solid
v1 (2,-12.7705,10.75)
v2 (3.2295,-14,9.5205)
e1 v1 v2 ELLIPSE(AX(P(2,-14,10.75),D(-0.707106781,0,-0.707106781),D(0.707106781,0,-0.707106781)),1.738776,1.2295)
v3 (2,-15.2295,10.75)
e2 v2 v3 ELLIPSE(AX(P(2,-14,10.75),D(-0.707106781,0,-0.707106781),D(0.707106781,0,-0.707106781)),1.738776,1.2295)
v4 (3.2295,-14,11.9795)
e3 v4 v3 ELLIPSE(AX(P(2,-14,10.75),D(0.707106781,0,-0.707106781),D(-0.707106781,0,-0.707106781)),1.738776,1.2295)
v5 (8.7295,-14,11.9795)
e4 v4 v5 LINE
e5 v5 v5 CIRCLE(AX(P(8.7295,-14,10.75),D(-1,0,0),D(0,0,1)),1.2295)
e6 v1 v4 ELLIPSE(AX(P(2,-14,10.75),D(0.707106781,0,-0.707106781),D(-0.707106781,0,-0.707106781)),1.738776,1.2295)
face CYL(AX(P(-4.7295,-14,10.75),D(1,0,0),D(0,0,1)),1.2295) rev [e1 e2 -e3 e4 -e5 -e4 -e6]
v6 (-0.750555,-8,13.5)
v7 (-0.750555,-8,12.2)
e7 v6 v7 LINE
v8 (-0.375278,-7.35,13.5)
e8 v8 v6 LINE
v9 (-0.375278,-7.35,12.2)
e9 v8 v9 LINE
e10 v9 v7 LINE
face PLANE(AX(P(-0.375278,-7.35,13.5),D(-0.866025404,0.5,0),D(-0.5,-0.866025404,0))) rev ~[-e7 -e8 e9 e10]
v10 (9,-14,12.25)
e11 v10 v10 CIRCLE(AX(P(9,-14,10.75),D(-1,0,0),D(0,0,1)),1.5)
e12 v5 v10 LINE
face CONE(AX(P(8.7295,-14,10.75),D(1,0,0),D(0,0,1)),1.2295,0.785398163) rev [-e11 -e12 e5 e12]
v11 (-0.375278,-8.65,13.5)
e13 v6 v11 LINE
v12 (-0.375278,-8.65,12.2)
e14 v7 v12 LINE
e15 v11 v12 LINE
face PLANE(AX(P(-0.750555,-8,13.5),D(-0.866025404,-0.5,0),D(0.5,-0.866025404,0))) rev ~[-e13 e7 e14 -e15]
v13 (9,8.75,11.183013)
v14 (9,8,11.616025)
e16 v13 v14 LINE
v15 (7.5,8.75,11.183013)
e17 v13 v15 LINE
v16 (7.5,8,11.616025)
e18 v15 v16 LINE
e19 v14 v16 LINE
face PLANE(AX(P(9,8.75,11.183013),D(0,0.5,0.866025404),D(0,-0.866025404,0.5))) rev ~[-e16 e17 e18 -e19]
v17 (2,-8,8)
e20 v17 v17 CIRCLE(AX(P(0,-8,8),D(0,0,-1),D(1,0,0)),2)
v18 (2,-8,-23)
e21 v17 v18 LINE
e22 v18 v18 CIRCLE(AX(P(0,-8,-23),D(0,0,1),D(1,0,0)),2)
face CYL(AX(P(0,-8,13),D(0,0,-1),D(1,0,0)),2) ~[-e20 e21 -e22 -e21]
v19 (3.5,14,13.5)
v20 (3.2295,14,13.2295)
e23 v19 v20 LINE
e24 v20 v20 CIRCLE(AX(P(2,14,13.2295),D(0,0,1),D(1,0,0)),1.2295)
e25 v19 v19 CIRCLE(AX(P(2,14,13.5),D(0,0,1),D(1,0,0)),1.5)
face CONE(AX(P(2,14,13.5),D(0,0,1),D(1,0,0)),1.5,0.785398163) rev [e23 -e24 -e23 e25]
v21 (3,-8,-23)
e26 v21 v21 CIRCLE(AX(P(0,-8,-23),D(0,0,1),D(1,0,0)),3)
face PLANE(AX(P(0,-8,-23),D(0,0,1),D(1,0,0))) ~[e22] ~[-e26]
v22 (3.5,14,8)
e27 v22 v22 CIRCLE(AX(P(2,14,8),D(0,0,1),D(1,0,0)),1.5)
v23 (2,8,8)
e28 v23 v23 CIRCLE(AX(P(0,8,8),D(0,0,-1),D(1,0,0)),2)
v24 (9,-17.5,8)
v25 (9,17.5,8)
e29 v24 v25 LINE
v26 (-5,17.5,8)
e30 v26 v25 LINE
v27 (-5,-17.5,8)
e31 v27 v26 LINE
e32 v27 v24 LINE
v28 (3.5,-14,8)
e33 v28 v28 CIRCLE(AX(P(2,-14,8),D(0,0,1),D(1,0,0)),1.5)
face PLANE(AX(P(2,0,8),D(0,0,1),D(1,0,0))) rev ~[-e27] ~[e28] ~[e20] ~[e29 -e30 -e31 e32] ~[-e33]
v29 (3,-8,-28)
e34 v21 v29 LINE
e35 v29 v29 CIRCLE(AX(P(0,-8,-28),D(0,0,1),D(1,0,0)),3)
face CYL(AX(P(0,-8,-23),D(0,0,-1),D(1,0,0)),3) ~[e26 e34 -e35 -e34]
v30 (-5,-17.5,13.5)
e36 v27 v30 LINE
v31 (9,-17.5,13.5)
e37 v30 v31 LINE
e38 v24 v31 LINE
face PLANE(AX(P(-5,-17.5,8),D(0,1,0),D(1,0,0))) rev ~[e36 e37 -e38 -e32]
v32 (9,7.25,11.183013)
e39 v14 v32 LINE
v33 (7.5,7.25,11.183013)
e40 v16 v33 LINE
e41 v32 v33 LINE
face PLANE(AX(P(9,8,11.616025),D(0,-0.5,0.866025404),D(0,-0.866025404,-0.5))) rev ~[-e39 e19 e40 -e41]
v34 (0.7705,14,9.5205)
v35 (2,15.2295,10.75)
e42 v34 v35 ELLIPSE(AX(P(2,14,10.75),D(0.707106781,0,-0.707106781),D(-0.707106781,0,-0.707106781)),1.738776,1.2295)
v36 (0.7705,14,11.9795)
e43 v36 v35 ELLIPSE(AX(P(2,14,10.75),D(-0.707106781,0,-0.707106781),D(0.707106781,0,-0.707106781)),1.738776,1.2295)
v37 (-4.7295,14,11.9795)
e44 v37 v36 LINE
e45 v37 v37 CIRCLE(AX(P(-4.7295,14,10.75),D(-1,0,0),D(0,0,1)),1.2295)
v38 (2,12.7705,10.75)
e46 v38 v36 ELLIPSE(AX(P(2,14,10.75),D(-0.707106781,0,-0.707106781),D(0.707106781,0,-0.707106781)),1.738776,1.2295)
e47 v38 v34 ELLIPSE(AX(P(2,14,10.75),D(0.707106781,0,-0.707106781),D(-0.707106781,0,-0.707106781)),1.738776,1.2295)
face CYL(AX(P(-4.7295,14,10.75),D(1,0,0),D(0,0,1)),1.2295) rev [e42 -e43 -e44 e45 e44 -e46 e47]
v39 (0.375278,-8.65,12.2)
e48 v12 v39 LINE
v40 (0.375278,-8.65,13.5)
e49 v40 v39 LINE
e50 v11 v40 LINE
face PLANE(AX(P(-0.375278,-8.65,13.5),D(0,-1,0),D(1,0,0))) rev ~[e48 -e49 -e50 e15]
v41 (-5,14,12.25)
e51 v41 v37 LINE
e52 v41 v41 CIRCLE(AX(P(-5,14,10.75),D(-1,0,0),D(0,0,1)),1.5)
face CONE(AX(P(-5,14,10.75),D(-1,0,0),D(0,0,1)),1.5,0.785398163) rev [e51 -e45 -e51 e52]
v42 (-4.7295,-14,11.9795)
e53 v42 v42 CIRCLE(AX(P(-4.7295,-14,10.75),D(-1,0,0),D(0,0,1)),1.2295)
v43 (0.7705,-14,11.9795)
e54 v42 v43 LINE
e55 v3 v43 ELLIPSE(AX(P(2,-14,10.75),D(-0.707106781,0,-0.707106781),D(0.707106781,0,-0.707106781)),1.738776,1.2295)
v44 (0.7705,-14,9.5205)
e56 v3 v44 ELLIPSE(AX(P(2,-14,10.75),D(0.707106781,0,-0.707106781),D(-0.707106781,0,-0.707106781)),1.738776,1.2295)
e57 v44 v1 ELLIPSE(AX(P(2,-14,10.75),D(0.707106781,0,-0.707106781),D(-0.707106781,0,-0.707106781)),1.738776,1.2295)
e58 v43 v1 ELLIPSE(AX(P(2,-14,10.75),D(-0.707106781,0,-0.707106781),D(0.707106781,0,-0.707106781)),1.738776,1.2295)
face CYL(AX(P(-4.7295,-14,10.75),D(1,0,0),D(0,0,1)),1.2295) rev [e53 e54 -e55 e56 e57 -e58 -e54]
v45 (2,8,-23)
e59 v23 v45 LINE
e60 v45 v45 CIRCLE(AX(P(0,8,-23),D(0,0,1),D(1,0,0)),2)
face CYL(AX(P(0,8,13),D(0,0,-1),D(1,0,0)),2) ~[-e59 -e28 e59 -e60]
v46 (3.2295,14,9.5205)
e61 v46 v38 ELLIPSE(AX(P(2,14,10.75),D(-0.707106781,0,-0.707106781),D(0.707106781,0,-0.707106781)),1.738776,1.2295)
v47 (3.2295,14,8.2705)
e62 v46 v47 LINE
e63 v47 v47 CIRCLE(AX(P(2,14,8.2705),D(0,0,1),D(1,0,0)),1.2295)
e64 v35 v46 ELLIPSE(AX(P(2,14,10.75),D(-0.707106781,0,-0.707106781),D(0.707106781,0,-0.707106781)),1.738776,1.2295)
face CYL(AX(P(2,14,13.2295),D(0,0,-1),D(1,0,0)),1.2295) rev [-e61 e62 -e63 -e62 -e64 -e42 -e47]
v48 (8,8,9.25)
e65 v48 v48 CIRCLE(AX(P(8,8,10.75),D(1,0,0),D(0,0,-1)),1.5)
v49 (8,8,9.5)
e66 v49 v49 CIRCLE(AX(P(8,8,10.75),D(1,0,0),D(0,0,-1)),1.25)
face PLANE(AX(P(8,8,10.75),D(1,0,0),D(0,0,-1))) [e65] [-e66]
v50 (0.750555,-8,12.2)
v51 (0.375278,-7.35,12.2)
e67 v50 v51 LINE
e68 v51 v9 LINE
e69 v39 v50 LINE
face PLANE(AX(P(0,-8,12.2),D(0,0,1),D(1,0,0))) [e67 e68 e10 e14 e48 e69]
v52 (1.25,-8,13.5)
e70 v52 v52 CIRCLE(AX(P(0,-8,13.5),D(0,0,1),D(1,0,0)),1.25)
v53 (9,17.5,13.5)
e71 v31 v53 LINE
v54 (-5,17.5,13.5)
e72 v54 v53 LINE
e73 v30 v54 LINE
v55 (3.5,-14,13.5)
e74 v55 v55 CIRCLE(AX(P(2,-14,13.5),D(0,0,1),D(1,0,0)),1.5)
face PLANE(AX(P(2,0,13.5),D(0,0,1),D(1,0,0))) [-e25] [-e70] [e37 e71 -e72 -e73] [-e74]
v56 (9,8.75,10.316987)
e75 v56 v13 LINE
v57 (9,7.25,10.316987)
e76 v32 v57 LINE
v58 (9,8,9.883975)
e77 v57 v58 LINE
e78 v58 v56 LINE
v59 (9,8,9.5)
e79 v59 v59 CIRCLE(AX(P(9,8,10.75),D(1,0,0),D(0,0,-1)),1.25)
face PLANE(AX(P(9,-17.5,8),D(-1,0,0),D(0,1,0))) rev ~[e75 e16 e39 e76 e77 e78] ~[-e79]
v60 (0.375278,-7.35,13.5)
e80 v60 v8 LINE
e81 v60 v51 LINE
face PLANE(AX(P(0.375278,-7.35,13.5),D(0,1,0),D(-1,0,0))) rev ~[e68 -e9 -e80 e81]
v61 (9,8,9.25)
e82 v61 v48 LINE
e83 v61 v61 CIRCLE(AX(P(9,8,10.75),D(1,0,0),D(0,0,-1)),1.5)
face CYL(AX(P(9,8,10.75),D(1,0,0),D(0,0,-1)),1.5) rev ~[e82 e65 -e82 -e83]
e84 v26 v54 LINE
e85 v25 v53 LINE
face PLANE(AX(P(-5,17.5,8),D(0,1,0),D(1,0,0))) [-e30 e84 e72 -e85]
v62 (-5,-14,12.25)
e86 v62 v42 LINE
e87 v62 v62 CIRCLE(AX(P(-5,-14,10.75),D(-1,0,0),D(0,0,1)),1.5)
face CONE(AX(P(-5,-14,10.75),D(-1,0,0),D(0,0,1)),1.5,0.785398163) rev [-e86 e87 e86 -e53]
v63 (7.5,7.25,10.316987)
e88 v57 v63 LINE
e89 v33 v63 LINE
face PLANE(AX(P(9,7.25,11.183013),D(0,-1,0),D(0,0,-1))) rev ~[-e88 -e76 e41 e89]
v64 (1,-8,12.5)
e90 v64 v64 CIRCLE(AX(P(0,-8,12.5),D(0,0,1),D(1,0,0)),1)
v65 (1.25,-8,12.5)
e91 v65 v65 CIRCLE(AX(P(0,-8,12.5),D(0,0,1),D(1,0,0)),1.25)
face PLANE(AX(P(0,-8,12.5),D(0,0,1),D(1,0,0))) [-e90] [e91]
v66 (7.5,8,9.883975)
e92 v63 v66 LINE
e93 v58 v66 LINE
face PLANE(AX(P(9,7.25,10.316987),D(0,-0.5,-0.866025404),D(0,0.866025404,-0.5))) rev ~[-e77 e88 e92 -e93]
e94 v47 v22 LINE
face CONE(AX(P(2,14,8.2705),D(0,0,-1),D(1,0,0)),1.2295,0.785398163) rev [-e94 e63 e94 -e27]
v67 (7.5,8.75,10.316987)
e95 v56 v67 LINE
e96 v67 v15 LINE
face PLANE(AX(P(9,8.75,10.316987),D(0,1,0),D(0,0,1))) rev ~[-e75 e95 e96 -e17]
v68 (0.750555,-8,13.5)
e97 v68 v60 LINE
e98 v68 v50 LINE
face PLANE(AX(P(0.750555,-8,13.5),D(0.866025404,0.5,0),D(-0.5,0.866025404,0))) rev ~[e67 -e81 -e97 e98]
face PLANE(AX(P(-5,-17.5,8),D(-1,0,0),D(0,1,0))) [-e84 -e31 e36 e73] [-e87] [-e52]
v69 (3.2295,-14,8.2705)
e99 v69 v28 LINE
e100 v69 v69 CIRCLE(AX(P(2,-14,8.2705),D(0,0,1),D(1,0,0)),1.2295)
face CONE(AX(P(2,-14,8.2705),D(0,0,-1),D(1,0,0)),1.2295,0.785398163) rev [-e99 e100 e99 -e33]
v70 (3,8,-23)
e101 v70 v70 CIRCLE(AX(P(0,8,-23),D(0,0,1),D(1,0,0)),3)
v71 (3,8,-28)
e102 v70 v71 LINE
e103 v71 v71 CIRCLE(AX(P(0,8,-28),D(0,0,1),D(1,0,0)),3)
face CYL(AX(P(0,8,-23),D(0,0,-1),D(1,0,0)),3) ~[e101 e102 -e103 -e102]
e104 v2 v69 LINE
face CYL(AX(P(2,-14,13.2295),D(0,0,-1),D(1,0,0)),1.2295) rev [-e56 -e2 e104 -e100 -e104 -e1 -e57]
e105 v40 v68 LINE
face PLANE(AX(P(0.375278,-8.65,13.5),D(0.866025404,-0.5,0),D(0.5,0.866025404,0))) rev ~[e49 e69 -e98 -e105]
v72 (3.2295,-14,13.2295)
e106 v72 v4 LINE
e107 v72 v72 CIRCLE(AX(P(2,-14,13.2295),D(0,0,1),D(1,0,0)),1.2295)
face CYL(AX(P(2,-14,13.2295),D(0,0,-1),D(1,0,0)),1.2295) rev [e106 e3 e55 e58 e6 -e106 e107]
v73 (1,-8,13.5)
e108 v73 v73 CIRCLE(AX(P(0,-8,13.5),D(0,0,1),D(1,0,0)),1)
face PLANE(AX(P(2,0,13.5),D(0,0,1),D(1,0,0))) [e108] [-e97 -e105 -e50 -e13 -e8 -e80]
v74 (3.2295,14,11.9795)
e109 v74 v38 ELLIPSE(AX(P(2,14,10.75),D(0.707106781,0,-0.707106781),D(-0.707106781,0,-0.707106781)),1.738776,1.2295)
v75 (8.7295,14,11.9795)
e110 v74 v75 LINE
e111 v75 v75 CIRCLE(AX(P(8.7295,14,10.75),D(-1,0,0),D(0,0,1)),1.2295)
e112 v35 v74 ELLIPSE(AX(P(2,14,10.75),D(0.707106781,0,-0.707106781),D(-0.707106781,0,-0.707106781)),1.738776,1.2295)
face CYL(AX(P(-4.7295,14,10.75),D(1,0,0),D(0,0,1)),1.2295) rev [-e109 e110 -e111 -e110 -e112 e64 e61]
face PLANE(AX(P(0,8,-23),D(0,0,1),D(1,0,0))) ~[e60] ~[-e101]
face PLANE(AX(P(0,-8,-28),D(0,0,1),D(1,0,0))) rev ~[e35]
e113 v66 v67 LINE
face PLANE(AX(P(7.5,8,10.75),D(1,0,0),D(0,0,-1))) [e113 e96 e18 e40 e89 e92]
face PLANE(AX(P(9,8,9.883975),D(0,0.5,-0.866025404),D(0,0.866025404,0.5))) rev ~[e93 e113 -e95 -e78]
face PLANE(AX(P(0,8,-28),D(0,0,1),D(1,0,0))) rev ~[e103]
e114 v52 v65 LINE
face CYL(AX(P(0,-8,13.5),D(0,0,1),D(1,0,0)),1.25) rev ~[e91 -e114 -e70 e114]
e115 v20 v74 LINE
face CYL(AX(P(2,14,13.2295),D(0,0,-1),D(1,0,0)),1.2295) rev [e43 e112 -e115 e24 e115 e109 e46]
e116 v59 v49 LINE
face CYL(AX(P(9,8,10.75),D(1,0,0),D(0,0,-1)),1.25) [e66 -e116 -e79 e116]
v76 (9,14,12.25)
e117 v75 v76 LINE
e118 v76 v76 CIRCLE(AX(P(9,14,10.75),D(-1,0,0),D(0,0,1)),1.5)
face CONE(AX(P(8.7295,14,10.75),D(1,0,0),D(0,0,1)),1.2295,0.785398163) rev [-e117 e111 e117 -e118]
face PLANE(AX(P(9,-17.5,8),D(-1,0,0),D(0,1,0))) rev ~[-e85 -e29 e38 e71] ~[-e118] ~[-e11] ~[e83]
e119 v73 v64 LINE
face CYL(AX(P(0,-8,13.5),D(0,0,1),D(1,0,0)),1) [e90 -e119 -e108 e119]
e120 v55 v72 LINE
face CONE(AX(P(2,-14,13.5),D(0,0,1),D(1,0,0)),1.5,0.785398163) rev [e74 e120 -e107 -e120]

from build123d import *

# Parameters (mm, degrees)
SKETCH1_W           = 14
SKETCH1_H           = 35
BOSS_EXTRUDE1_DEPTH = 5.5
SKETCH8_R           = 1.25
SKETCH8_R_2         = 1
CUT_EXTRUDE1_DEPTH  = 1
CUT_EXTRUDE2_DEPTH  = 1.3
SKETCH10_R          = 1.5
SKETCH10_R_2        = 1.25
CUT_EXTRUDE3_DEPTH  = 1
CUT_EXTRUDE4_DEPTH  = 1.5


with BuildPart() as part:
    # Sketch1 → Boss-Extrude1 (new body)
    with BuildSketch(Plane.XY.offset(8)):
        with Locations((2, 0)):
            Rectangle(SKETCH1_W, SKETCH1_H)
    extrude(amount=BOSS_EXTRUDE1_DEPTH)

    # Sketch2 → Revolve1 (revolve)
    with BuildSketch(Plane(origin=(0, 0, 0), x_dir=(0, 0, -1), z_dir=(1, 0, 0)), mode=Mode.PRIVATE) as revolve1_sk:
        Polygon((-13, 8), (-13, 10), (23, 10), (23, 11), (28, 11), (28, 8), align=None)
    revolve(revolve1_sk.sketch.rotate(Axis((0, 8, -28), (0, 0, 1)), 270), axis=Axis((0, 8, -28), (0, 0, 1)))

    # Sketch3 → Revolve2 (revolve)
    with BuildSketch(Plane(origin=(0, 0, 0), x_dir=(0, 0, -1), z_dir=(1, 0, 0)), mode=Mode.PRIVATE) as revolve2_sk:
        Polygon((-13, -8), (-13, -6), (23, -6), (23, -5), (28, -5), (28, -8), align=None)
    revolve(revolve2_sk.sketch.rotate(Axis((0, -8, -28), (0, 0, 1)), 270), axis=Axis((0, -8, -28), (0, 0, 1)))

    # Sketch4 → Cut-Revolve1 (revolve, cut)
    with BuildSketch(Plane(origin=(2, 0, 0), x_dir=(0, 0, -1), z_dir=(1, 0, 0)), mode=Mode.PRIVATE) as cut_revolve1_sk:
        Polygon((-13.5, 14), (-13.5, 15.5), (-13.2295, 15.2295), (-8.2705, 15.2295), (-8, 15.5), (-8, 14), align=None)
    revolve(cut_revolve1_sk.sketch.rotate(Axis((2, 14, 8), (0, 0, 1)), 270), axis=Axis((2, 14, 8), (0, 0, 1)), mode=Mode.SUBTRACT)

    # Sketch5 → Cut-Revolve2 (revolve, cut)
    with BuildSketch(Plane(origin=(2, 0, 0), x_dir=(0, 0, -1), z_dir=(1, 0, 0)), mode=Mode.PRIVATE) as cut_revolve2_sk:
        Polygon((-13.5, -14), (-13.5, -12.5), (-13.2295, -12.7705), (-8.2705, -12.7705), (-8, -12.5), (-8, -14), align=None)
    revolve(cut_revolve2_sk.sketch.rotate(Axis((2, -14, 8), (0, 0, 1)), 270), axis=Axis((2, -14, 8), (0, 0, 1)), mode=Mode.SUBTRACT)

    # Sketch6 → Cut-Revolve3 (revolve, cut)
    with BuildSketch(Plane.XY.offset(10.75), mode=Mode.PRIVATE) as cut_revolve3_sk:
        Polygon((-5, 14), (-5, 15.5), (-4.7295, 15.2295), (8.7295, 15.2295), (9, 15.5), (9, 14), align=None)
    revolve(cut_revolve3_sk.sketch.rotate(Axis((9, 14, 10.75), (-1, 0, 0)), 270), axis=Axis((9, 14, 10.75), (-1, 0, 0)), mode=Mode.SUBTRACT)

    # Sketch7 → Cut-Revolve4 (revolve, cut)
    with BuildSketch(Plane.XY.offset(10.75), mode=Mode.PRIVATE) as cut_revolve4_sk:
        Polygon((-5, -14), (-5, -12.5), (-4.7295, -12.7705), (8.7295, -12.7705), (9, -12.5), (9, -14), align=None)
    revolve(cut_revolve4_sk.sketch.rotate(Axis((9, -14, 10.75), (-1, 0, 0)), 270), axis=Axis((9, -14, 10.75), (-1, 0, 0)), mode=Mode.SUBTRACT)

    # Sketch8 → Cut-Extrude1 (cut)
    with BuildSketch(Plane.XY.offset(13.5)):
        with Locations((0, -8)):
            Circle(SKETCH8_R)
        with Locations((0, -8)):
            Circle(SKETCH8_R_2, mode=Mode.SUBTRACT)
    extrude(amount=-CUT_EXTRUDE1_DEPTH, mode=Mode.SUBTRACT)

    # Sketch9 → Cut-Extrude2 (cut)
    with BuildSketch(Plane.XY.offset(13.5)):
        Polygon((-0.75055535, -8), (-0.375277675, -8.65), (0.375277675, -8.65), (0.75055535, -8), (0.375277675, -7.35), (-0.375277675, -7.35), align=None)
    extrude(amount=-CUT_EXTRUDE2_DEPTH, mode=Mode.SUBTRACT)

    # Sketch10 → Cut-Extrude3 (cut)
    with BuildSketch(Plane(origin=(9, 0, 0), x_dir=(0, 0, -1), z_dir=(1, 0, 0))):
        with Locations((-10.75, 8)):
            Circle(SKETCH10_R)
        with Locations((-10.75, 8)):
            Circle(SKETCH10_R_2, mode=Mode.SUBTRACT)
    extrude(amount=-CUT_EXTRUDE3_DEPTH, mode=Mode.SUBTRACT)

    # Sketch11 → Cut-Extrude4 (cut)
    with BuildSketch(Plane(origin=(9, 0, 0), x_dir=(0, 0, -1), z_dir=(1, 0, 0))):
        Polygon((-11.616025404, 8), (-11.183012702, 7.25), (-10.316987298, 7.25), (-9.883974596, 8), (-10.316987298, 8.75), (-11.183012702, 8.75), align=None)
    extrude(amount=-CUT_EXTRUDE4_DEPTH, mode=Mode.SUBTRACT)


solid = part.part
